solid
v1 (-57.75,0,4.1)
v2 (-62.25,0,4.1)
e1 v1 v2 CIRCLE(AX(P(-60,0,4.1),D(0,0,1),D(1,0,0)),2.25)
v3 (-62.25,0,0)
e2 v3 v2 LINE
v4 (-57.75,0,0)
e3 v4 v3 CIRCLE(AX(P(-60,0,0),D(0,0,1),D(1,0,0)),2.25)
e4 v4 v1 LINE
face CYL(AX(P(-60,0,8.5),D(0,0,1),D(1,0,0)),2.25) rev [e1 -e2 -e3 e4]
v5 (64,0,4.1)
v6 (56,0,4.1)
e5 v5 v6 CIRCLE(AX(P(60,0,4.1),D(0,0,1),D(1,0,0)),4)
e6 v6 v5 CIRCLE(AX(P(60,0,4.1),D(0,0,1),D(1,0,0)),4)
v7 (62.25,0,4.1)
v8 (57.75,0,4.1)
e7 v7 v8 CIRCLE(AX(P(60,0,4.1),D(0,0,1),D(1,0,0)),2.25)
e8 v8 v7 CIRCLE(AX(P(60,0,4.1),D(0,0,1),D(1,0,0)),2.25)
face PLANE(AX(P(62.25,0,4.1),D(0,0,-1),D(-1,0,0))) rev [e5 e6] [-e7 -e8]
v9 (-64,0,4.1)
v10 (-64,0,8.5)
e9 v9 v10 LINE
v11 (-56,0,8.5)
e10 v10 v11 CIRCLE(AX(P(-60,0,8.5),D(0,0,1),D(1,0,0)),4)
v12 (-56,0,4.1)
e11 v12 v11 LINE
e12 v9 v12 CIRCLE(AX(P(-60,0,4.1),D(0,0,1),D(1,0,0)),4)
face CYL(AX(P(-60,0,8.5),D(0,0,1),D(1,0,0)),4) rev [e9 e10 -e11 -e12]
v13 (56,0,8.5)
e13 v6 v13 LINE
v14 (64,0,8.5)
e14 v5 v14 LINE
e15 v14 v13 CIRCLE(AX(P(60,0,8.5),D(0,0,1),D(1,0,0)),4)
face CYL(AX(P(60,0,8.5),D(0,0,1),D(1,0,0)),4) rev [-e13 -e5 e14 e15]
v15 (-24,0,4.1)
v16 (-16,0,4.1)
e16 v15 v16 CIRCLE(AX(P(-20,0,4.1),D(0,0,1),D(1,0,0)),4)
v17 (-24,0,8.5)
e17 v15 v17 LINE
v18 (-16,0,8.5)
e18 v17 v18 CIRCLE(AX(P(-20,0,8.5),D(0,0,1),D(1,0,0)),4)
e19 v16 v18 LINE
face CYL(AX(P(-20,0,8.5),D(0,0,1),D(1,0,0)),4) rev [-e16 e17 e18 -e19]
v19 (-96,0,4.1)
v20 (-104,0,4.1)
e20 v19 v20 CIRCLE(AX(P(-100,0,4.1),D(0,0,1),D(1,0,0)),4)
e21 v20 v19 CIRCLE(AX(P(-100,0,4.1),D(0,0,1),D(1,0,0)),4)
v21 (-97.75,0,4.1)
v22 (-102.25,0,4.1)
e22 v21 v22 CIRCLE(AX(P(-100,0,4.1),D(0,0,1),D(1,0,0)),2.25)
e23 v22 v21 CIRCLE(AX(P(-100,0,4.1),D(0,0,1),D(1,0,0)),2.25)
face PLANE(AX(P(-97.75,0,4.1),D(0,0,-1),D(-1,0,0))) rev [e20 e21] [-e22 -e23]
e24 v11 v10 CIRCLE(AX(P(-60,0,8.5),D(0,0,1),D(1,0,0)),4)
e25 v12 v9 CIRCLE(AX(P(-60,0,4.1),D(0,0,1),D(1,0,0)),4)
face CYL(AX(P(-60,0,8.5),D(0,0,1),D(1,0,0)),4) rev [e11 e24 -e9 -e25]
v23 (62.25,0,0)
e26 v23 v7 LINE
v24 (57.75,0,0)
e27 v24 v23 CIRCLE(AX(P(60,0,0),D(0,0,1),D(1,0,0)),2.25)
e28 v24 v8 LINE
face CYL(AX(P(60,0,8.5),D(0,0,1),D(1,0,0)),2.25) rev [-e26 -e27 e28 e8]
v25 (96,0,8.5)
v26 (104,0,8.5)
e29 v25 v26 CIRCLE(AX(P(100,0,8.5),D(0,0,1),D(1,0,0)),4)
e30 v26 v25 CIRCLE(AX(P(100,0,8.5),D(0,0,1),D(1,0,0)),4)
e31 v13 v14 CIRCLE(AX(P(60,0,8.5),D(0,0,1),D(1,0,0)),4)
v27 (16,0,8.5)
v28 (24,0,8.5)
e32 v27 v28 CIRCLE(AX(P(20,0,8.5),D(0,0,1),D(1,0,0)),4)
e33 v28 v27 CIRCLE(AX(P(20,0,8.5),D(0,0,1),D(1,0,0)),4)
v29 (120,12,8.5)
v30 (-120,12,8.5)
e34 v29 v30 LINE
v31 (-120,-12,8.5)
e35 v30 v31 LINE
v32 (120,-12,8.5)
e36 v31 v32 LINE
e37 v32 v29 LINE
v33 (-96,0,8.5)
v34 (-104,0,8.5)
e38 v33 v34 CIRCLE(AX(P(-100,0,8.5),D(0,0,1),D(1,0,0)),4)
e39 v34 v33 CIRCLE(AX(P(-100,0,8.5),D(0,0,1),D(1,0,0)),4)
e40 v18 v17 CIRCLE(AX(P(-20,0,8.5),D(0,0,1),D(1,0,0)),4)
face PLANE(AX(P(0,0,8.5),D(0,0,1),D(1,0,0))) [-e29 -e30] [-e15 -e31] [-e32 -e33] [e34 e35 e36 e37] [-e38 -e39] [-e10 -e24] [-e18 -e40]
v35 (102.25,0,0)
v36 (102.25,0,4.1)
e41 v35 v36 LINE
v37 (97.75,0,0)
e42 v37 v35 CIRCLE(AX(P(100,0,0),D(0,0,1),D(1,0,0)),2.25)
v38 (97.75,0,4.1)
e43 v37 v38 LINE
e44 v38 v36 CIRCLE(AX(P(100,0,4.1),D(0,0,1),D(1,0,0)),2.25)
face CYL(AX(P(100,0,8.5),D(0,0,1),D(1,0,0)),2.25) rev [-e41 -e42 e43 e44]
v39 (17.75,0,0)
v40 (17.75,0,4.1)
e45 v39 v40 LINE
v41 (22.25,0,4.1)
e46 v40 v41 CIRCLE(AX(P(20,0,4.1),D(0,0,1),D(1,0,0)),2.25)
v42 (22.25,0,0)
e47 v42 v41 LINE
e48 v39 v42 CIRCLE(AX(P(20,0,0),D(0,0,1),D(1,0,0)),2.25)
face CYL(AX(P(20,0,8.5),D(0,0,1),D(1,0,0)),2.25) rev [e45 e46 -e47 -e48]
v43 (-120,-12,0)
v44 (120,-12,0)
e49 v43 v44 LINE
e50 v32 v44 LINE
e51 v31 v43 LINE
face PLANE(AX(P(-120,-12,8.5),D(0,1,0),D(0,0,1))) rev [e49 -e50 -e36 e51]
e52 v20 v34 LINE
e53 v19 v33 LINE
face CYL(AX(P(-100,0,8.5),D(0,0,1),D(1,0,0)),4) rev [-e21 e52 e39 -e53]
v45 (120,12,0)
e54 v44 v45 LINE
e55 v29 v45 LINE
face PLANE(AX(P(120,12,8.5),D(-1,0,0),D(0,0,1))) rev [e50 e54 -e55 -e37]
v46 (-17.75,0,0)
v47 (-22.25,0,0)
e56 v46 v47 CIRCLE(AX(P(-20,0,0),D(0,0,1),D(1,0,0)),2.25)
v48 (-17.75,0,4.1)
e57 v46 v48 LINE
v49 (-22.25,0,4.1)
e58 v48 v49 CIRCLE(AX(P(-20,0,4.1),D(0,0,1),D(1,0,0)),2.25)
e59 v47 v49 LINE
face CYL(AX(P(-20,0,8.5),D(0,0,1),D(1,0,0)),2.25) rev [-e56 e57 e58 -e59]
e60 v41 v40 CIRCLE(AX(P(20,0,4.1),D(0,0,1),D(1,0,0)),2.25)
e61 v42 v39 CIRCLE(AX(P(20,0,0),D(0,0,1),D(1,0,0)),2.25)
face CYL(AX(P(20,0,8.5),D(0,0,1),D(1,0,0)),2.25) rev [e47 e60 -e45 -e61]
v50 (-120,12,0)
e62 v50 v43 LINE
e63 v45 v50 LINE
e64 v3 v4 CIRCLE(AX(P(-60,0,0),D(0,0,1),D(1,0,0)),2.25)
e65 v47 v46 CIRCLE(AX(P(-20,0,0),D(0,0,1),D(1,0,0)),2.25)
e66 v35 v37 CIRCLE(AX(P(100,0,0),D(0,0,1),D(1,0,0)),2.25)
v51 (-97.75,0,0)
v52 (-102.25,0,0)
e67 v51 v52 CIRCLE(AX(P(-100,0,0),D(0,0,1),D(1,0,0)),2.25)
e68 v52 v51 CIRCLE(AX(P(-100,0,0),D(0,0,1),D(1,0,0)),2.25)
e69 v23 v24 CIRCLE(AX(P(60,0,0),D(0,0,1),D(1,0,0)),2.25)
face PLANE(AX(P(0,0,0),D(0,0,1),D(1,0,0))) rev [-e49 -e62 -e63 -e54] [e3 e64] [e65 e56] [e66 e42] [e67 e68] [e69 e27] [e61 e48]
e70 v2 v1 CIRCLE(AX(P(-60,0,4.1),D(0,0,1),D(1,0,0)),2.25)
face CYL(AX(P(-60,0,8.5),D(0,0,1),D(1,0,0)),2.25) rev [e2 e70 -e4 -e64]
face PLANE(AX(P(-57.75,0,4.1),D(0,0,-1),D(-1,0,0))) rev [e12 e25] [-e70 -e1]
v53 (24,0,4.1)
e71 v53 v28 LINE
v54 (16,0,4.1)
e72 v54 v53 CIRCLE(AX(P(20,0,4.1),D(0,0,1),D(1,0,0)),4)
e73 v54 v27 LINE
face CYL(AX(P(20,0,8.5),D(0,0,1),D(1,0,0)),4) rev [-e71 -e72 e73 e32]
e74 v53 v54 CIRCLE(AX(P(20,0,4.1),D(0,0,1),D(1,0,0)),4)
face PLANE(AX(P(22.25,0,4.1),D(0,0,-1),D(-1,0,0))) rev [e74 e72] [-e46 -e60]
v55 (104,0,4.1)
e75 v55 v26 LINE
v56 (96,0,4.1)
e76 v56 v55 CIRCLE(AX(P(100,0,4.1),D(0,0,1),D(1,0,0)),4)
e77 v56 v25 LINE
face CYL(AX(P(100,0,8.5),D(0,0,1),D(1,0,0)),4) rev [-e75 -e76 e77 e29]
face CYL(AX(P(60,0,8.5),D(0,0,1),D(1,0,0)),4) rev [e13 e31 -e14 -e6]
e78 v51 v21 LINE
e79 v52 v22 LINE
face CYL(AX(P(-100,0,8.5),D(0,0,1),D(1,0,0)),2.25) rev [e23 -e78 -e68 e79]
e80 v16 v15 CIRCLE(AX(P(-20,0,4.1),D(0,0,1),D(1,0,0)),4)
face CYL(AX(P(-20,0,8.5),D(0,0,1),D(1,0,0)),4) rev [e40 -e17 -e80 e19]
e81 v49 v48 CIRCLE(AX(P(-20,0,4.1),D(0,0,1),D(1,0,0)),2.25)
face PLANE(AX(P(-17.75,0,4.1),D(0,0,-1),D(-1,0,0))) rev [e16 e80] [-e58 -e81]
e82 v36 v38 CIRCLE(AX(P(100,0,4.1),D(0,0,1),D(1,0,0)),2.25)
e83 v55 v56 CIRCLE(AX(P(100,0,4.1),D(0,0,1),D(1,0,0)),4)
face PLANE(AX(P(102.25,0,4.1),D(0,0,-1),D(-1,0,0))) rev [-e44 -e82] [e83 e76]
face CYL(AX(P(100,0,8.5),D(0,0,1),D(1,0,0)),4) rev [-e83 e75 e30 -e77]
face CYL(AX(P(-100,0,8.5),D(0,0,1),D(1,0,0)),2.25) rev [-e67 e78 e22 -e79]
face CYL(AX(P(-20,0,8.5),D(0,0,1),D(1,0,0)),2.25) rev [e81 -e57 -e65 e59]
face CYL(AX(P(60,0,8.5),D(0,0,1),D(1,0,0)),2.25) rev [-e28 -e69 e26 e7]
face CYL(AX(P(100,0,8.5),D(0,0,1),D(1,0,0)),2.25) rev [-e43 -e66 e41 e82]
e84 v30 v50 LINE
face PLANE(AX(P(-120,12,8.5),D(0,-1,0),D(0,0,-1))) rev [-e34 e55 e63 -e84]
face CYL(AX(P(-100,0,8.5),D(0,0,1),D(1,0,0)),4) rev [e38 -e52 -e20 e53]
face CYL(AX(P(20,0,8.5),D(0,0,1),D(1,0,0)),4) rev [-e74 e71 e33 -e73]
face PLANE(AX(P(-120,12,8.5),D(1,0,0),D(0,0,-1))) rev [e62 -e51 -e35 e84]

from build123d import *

# Parameters (mm, degrees)
SKETCH1_W                                           = 240
SKETCH1_H                                           = 24
BOSS_EXTRUDE1_DEPTH                                 = 8.5
CBORE_FOR_M4_HEX_SOCKET_HEAD_CAP_SCREW1_D           = 4.5
CBORE_FOR_M4_HEX_SOCKET_HEAD_CAP_SCREW1_CBORE_D     = 8
CBORE_FOR_M4_HEX_SOCKET_HEAD_CAP_SCREW1_CBORE_DEPTH = 4.4
LPATTERN1_COUNT                                     = 6
LPATTERN1_PITCH                                     = 40


with BuildPart() as part:
    # Sketch1 → Boss-Extrude1 (new body)
    with BuildSketch(Plane.XY):
        Rectangle(SKETCH1_W, SKETCH1_H)
    extrude(amount=BOSS_EXTRUDE1_DEPTH)

    # CBORE for M4 Hex Socket Head Cap Screw1 (through all)
    with Locations(Plane.XY.offset(8.5)):
        with Locations((-100, 0)):
            cbore_for_m4_hex_socket_head_cap_screw1 = CounterBoreHole(CBORE_FOR_M4_HEX_SOCKET_HEAD_CAP_SCREW1_D / 2, CBORE_FOR_M4_HEX_SOCKET_HEAD_CAP_SCREW1_CBORE_D / 2, CBORE_FOR_M4_HEX_SOCKET_HEAD_CAP_SCREW1_CBORE_DEPTH)

    # LPattern1: CBORE for M4 Hex Socket Head Cap Screw1 ×6
    with Locations(*[(i * LPATTERN1_PITCH, 0, 0) for i in range(1, LPATTERN1_COUNT)]):
        add(cbore_for_m4_hex_socket_head_cap_screw1, mode=Mode.SUBTRACT)


solid = part.part
